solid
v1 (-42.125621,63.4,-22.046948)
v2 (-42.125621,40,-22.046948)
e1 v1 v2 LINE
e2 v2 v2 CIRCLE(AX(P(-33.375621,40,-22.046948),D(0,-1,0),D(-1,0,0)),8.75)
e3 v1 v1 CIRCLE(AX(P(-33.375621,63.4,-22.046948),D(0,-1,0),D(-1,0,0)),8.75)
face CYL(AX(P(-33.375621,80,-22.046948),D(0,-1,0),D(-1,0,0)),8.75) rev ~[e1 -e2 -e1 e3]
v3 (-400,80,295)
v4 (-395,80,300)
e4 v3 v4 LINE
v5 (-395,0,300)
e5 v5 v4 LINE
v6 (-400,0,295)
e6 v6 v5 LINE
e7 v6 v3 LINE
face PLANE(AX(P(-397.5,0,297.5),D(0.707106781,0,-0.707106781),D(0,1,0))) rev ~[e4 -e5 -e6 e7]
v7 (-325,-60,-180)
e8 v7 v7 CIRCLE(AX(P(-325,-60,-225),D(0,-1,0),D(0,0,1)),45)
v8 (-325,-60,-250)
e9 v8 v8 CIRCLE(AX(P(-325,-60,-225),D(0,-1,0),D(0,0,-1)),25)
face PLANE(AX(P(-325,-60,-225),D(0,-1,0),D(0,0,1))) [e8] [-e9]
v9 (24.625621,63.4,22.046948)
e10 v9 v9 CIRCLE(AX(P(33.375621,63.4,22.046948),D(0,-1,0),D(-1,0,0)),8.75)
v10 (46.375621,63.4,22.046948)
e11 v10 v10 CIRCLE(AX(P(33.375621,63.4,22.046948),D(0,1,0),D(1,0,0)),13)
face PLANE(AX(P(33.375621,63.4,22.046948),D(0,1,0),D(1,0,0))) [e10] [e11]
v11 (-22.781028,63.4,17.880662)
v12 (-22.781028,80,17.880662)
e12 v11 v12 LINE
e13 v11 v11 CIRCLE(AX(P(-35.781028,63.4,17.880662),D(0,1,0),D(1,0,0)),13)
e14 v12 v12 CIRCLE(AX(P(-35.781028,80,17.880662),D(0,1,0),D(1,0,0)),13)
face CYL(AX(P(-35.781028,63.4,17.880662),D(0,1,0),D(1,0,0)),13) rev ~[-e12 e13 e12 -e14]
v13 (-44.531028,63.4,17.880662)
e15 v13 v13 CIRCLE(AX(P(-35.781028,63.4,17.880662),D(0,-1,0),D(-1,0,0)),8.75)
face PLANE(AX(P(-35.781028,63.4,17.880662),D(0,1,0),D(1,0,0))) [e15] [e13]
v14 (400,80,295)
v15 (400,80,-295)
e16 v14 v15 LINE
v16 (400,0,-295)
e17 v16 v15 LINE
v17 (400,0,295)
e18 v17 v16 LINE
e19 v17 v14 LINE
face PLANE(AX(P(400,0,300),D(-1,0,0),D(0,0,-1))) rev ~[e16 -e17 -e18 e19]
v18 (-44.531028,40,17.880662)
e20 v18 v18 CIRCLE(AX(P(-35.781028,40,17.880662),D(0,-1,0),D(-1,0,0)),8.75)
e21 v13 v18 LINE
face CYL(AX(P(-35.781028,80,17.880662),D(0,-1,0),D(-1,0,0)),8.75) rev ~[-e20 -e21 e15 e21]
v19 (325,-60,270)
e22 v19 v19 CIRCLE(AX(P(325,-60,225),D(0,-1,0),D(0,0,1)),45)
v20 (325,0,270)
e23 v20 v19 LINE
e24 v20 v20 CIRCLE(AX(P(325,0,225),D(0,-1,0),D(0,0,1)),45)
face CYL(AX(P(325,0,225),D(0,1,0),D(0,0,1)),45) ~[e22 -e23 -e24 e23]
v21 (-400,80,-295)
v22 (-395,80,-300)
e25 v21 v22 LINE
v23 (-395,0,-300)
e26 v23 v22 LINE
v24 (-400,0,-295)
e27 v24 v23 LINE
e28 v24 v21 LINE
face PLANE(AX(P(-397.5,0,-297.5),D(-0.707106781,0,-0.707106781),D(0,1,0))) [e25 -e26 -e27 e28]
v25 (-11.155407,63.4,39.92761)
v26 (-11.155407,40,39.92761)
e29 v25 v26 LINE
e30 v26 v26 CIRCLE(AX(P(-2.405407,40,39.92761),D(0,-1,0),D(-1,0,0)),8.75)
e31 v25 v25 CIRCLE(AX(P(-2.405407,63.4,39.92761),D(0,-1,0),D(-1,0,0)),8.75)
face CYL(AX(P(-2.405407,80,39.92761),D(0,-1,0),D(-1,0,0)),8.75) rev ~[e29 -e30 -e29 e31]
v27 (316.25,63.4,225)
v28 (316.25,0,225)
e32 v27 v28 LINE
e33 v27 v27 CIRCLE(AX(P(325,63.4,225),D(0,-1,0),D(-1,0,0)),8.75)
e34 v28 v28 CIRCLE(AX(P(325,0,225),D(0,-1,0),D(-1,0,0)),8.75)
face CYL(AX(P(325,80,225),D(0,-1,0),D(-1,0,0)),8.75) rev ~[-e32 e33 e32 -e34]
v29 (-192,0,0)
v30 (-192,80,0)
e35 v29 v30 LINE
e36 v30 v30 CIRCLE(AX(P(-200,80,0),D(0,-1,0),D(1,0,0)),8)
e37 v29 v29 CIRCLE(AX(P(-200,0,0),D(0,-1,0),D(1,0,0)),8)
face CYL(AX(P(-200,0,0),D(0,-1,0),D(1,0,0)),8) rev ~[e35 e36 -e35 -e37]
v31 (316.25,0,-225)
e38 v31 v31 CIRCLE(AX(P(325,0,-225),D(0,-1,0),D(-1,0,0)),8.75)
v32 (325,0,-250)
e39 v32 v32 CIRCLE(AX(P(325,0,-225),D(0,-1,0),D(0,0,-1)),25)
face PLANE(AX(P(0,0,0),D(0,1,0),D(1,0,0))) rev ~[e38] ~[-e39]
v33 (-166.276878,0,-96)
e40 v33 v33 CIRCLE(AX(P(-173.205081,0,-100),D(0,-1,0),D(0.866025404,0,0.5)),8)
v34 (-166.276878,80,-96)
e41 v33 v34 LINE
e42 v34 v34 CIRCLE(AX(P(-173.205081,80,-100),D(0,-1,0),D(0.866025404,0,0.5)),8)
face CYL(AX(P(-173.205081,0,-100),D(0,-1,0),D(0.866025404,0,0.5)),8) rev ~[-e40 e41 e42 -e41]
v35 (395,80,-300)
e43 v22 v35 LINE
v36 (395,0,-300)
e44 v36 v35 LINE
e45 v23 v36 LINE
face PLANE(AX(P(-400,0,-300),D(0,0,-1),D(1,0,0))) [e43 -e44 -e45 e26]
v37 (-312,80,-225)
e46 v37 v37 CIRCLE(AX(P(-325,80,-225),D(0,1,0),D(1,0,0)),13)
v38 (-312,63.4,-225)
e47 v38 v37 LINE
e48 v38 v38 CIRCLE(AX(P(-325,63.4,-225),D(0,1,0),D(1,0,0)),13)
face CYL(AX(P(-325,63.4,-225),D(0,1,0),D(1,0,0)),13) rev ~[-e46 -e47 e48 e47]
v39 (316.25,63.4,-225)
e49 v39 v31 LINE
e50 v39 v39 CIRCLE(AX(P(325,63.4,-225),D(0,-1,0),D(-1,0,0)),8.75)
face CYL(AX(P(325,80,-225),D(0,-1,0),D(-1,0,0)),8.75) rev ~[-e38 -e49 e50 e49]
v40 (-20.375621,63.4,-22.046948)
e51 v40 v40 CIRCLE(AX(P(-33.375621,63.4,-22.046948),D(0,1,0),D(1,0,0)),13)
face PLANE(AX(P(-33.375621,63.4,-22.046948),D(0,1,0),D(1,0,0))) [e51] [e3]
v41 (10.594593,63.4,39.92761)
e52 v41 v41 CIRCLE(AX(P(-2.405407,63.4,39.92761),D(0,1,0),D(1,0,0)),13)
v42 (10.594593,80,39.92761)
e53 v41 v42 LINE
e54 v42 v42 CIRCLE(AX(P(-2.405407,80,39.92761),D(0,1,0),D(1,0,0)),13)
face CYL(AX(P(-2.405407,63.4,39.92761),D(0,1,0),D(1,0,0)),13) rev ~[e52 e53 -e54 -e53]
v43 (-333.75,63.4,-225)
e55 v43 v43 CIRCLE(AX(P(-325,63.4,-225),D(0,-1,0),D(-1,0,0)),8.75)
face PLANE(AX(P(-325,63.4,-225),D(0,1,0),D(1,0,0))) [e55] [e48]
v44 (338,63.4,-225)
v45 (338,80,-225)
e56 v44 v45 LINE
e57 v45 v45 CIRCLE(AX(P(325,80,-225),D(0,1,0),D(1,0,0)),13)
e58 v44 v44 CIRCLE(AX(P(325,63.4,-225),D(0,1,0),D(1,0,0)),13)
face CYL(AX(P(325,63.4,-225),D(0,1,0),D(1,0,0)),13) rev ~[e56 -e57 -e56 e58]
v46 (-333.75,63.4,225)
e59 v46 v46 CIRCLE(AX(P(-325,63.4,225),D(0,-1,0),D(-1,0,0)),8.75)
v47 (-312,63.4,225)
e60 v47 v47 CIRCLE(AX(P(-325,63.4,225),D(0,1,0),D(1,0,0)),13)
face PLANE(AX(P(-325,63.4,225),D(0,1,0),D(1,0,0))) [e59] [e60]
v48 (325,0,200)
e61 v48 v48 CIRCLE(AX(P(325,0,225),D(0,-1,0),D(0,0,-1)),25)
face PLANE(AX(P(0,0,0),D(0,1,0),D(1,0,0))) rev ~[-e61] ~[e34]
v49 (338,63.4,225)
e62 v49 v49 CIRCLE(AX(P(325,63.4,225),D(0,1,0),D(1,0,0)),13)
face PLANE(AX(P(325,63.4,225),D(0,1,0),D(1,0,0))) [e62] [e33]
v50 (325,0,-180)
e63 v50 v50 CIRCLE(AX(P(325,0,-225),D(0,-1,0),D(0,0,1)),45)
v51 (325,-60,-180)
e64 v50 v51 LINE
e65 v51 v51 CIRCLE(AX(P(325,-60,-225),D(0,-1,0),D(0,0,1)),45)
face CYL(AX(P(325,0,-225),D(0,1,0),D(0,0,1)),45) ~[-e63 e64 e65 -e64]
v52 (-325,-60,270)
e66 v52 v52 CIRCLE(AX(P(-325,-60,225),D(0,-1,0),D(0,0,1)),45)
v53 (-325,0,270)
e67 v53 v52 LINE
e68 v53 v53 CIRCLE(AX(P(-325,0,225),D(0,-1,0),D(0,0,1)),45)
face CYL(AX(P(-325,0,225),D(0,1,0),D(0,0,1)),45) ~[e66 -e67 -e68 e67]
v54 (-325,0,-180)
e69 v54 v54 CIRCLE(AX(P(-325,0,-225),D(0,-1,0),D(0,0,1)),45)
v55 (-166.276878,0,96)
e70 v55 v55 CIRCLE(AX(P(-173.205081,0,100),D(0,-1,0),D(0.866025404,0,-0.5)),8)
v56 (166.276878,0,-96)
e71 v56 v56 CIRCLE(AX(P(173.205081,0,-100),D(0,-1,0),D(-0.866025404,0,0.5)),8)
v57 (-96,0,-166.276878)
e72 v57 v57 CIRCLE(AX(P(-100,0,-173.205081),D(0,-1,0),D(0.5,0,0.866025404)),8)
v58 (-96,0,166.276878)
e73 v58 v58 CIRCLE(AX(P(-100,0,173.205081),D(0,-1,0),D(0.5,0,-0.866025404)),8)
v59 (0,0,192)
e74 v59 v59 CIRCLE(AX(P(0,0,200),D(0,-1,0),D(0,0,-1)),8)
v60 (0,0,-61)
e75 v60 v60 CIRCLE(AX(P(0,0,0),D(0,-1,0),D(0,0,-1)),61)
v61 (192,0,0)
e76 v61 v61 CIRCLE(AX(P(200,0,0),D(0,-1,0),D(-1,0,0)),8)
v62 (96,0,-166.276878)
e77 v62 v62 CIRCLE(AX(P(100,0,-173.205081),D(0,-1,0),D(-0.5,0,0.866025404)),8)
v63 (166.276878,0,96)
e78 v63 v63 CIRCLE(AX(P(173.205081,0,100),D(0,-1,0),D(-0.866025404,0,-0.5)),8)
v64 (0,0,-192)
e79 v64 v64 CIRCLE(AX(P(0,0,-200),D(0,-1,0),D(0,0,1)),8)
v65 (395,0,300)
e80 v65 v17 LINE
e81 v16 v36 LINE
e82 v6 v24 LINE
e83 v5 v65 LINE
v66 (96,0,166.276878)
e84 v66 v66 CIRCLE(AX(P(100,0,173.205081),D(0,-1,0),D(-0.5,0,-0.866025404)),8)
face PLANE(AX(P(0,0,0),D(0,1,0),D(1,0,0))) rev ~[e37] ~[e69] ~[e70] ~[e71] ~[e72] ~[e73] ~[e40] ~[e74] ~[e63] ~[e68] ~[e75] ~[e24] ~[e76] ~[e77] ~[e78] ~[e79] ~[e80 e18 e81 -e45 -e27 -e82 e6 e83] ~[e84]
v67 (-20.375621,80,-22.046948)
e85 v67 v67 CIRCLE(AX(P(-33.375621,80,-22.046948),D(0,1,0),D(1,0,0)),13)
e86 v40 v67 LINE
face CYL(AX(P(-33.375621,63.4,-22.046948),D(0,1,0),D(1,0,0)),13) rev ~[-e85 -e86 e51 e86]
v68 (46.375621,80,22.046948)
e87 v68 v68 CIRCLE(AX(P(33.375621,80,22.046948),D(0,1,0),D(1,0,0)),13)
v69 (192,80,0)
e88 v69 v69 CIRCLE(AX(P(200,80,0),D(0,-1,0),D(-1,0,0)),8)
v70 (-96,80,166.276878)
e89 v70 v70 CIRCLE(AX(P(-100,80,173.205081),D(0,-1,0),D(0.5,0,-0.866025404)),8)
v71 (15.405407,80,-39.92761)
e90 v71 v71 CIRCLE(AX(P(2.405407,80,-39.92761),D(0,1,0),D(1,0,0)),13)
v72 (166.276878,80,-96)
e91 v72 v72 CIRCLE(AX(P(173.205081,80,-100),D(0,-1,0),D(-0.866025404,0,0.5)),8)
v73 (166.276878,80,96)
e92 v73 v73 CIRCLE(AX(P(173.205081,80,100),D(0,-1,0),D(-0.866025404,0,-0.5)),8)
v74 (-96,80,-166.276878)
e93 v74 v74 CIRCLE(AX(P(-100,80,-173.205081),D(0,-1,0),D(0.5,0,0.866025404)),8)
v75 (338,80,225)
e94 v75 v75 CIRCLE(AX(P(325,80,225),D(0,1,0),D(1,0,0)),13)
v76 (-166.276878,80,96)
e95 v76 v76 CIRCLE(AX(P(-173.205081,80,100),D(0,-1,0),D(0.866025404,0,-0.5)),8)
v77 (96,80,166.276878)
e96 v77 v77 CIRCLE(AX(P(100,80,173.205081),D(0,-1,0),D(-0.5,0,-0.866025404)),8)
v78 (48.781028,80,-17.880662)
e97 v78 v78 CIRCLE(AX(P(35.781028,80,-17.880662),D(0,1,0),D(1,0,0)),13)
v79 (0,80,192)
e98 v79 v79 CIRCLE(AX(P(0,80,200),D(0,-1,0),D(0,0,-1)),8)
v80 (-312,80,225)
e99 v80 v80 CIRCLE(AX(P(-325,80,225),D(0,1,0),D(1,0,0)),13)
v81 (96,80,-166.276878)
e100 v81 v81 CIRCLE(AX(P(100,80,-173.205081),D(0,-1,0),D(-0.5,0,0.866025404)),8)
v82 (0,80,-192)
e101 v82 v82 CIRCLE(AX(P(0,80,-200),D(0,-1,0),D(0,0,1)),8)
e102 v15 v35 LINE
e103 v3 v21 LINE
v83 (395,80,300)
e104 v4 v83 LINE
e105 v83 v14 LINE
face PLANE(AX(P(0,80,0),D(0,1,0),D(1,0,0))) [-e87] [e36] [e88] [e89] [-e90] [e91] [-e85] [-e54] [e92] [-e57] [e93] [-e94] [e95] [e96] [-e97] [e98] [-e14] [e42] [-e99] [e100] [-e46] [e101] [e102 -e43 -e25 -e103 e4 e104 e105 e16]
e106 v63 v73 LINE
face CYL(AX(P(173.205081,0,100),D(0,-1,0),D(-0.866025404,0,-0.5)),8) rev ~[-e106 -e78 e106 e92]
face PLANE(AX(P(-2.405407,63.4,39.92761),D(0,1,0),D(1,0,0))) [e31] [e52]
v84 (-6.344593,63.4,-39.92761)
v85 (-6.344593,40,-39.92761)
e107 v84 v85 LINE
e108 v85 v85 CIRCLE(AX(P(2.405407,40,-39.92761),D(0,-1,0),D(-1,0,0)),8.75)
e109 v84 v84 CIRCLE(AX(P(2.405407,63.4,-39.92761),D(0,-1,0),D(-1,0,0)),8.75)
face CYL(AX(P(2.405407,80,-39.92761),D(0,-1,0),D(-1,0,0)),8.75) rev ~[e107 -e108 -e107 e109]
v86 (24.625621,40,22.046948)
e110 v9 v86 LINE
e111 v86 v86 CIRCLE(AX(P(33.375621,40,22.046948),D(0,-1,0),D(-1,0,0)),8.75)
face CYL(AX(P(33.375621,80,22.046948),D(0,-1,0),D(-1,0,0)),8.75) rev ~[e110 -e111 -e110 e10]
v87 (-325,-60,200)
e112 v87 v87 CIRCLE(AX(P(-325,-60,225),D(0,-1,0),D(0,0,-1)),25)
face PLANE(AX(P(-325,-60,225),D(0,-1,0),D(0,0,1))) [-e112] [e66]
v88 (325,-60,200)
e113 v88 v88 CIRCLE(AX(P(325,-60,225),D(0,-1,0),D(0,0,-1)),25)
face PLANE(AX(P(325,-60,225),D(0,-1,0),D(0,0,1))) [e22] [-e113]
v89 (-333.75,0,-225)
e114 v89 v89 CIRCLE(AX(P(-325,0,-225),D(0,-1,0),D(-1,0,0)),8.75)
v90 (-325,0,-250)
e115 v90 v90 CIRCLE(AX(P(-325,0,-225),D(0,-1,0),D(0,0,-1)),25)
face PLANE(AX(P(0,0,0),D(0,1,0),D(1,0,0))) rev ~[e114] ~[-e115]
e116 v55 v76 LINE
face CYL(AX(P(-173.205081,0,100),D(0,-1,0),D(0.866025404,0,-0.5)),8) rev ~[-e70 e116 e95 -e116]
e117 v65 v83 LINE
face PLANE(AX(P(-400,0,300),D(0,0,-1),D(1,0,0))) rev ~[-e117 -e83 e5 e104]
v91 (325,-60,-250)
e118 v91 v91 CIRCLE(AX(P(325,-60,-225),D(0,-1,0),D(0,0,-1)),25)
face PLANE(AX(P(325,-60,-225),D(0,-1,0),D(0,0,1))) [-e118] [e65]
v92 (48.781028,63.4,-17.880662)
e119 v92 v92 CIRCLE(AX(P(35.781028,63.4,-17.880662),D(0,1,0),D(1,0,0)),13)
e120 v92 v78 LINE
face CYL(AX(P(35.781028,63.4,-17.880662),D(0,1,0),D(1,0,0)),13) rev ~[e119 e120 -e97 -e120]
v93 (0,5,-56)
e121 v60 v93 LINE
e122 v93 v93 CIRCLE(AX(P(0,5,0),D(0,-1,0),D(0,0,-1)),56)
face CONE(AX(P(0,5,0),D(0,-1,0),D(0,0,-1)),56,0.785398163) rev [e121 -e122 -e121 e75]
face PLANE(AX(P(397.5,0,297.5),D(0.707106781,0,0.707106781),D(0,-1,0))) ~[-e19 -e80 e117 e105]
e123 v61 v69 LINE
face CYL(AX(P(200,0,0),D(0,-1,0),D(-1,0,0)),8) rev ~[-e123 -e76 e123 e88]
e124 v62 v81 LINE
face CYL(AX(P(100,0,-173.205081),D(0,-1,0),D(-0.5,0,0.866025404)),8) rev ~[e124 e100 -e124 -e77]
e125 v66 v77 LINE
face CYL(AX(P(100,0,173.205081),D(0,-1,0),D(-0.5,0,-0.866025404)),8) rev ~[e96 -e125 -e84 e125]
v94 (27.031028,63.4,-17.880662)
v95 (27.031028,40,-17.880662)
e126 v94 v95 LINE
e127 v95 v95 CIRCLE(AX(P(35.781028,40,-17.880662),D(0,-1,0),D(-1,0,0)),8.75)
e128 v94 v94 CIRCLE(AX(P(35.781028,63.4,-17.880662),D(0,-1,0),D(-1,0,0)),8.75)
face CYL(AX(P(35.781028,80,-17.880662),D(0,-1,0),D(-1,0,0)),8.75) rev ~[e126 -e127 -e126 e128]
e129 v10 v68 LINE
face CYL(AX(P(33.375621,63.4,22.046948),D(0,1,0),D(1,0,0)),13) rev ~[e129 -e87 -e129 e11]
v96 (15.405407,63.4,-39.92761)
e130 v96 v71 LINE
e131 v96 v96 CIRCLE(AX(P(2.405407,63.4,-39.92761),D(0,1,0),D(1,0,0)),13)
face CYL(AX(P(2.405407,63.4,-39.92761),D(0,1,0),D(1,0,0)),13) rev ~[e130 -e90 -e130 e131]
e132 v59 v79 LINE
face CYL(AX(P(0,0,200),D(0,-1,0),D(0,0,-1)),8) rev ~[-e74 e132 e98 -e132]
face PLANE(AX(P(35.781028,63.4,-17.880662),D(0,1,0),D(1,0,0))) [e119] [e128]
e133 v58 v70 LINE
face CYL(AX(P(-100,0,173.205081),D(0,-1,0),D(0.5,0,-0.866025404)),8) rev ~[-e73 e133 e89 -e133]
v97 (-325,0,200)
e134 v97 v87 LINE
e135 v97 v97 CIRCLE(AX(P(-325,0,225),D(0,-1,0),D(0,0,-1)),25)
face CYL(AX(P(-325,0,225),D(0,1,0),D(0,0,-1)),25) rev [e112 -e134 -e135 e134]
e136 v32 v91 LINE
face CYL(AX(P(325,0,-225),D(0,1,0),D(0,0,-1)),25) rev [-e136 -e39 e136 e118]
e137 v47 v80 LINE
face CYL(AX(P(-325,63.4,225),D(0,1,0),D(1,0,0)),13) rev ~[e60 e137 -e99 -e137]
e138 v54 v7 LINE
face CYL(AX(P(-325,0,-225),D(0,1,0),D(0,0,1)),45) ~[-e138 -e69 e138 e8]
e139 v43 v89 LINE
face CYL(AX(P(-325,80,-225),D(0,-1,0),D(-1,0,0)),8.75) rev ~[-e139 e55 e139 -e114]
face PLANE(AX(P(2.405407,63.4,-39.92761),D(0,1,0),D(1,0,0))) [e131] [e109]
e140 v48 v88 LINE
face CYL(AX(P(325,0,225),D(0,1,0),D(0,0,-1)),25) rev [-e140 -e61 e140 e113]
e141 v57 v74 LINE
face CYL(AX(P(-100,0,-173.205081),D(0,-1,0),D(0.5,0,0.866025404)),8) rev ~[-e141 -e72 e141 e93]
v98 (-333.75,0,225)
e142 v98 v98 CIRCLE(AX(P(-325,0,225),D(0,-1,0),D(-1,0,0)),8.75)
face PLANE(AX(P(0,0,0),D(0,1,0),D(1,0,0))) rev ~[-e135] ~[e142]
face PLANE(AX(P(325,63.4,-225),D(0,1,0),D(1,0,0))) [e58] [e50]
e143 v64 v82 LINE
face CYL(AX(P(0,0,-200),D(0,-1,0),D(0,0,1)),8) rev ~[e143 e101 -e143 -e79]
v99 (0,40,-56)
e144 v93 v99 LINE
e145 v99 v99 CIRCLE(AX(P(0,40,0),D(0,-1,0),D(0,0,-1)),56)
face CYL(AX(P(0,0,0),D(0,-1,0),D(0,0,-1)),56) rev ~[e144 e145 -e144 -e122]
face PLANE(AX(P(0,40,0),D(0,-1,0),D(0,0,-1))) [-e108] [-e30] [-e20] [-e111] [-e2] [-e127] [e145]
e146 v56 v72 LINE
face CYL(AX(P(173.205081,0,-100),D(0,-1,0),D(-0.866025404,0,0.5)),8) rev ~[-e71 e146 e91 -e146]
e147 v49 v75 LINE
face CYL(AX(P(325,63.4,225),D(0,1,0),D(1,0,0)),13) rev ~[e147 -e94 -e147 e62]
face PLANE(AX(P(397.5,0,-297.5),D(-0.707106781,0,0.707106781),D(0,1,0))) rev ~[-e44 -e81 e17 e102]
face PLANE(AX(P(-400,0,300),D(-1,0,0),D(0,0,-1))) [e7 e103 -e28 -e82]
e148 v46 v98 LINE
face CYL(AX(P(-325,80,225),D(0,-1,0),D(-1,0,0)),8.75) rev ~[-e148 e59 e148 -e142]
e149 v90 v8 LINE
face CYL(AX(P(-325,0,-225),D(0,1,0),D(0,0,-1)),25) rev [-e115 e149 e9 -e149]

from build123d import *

# Parameters (mm, degrees)
SKETCH1_W                                            = 800
SKETCH1_H                                            = 600
BOSS_EXTRUDE1_DEPTH                                  = 80
CHAMFER1_SIZE                                        = 5
CBORE_FOR_M16_HEX_SOCKET_HEAD_CAP_SCREW1_D           = 17.5
CBORE_FOR_M16_HEX_SOCKET_HEAD_CAP_SCREW1_CBORE_D     = 26
CBORE_FOR_M16_HEX_SOCKET_HEAD_CAP_SCREW1_CBORE_DEPTH = 16.6
SKETCH4_R                                            = 56
CUT_EXTRUDE1_DEPTH                                   = 40
CHAMFER2_SIZE                                        = 5
SKETCH6_R                                            = 45
SKETCH6_R_2                                          = 25
BOSS_EXTRUDE2_DEPTH                                  = 60
CBORE_FOR_M16_HEX_SOCKET_HEAD_CAP_SCREW2_D           = 17.5
CBORE_FOR_M16_HEX_SOCKET_HEAD_CAP_SCREW2_CBORE_D     = 26
CBORE_FOR_M16_HEX_SOCKET_HEAD_CAP_SCREW2_CBORE_DEPTH = 16.6
SKETCH10_R                                           = 8
CUT_EXTRUDE2_DEPTH                                   = 507.359556047
CIRPATTERN1_COUNT                                    = 12


with BuildPart() as part:
    # Sketch1 → Boss-Extrude1 (new body)
    with BuildSketch(Plane(origin=(0, 0, 0), x_dir=(1, 0, 0), z_dir=(0, 1, 0))):
        Rectangle(SKETCH1_W, SKETCH1_H)
    extrude(amount=BOSS_EXTRUDE1_DEPTH)

    # Chamfer1
    chamfer1_edges = [part.edges().sort_by_distance(p)[0] for p in [
        (400, 40, 300),
        (-400, 40, 300),
        (-400, 40, -300),
        (400, 40, -300),
    ]]
    chamfer(chamfer1_edges, length=CHAMFER1_SIZE)

    # CBORE for M16 Hex Socket Head Cap Screw1 (through all)
    with Locations(Plane(origin=(0, 80, 0), x_dir=(1, 0, 0), z_dir=(0, 1, 0))):
        with Locations((2.405406629, 39.927609732), (35.781027655, 17.880661619), (33.375621026, -22.046948113), (-2.405406629, -39.927609732), (-35.781027655, -17.880661619), (-33.375621026, 22.046948113)):
            CounterBoreHole(CBORE_FOR_M16_HEX_SOCKET_HEAD_CAP_SCREW1_D / 2, CBORE_FOR_M16_HEX_SOCKET_HEAD_CAP_SCREW1_CBORE_D / 2, CBORE_FOR_M16_HEX_SOCKET_HEAD_CAP_SCREW1_CBORE_DEPTH)

    # Sketch4 → Cut-Extrude1 (cut)
    with BuildSketch(Plane.XZ):
        with Locations(Location((0, 0, 0), (0, 0, 270))):
            Circle(SKETCH4_R)
    extrude(amount=-CUT_EXTRUDE1_DEPTH, mode=Mode.SUBTRACT)

    # Chamfer2
    chamfer2_edges = [part.edges().sort_by_distance(p)[0] for p in [
        (0, 0, 56),
    ]]
    chamfer(chamfer2_edges, length=CHAMFER2_SIZE)

    # Sketch6 → Boss-Extrude2 (add)
    # profile 1 of 4: a face of its own
    with BuildSketch(Plane.XZ):
        with Locations(Location((-325, 225, 0), (0, 0, 90))):
            Circle(SKETCH6_R)
        with Locations(Location((-325, 225, 0), (0, 0, 270))):
            Circle(SKETCH6_R_2, mode=Mode.SUBTRACT)
    # profile 2 of 4: a face of its own
    with BuildSketch(Plane.XZ):
        with Locations(Location((325, 225, 0), (0, 0, 90))):
            Circle(SKETCH6_R)
        with Locations(Location((325, 225, 0), (0, 0, 270))):
            Circle(SKETCH6_R_2, mode=Mode.SUBTRACT)
    # profile 3 of 4: a face of its own
    with BuildSketch(Plane.XZ):
        with Locations(Location((-325, -225, 0), (0, 0, 90))):
            Circle(SKETCH6_R)
        with Locations(Location((-325, -225, 0), (0, 0, 270))):
            Circle(SKETCH6_R_2, mode=Mode.SUBTRACT)
    # profile 4 of 4: a face of its own
    with BuildSketch(Plane.XZ):
        with Locations(Location((325, -225, 0), (0, 0, 90))):
            Circle(SKETCH6_R)
        with Locations(Location((325, -225, 0), (0, 0, 270))):
            Circle(SKETCH6_R_2, mode=Mode.SUBTRACT)
    extrude(amount=BOSS_EXTRUDE2_DEPTH)

    # CBORE for M16 Hex Socket Head Cap Screw2 (through all)
    with Locations(Plane(origin=(0, 80, 0), x_dir=(1, 0, 0), z_dir=(0, 1, 0))):
        with Locations((-325, -225), (-325, 225), (325, 225), (325, -225)):
            CounterBoreHole(CBORE_FOR_M16_HEX_SOCKET_HEAD_CAP_SCREW2_D / 2, CBORE_FOR_M16_HEX_SOCKET_HEAD_CAP_SCREW2_CBORE_D / 2, CBORE_FOR_M16_HEX_SOCKET_HEAD_CAP_SCREW2_CBORE_DEPTH)

    # Sketch10 → Cut-Extrude2 (cut, through all)
    with BuildSketch(Plane.XZ):
        with Locations(Location((0, 200, 0), (0, 0, 270))):
            Circle(SKETCH10_R)
    cut_extrude2 = extrude(amount=-CUT_EXTRUDE2_DEPTH, mode=Mode.SUBTRACT)

    # CirPattern1: Cut-Extrude2 ×12 about axis
    cirpattern1_axis = Axis((0, 0, 0), (0, 1, 0))
    for i in range(1, CIRPATTERN1_COUNT):
        add(cut_extrude2.rotate(cirpattern1_axis, i * 360 / CIRPATTERN1_COUNT), mode=Mode.SUBTRACT)


solid = part.part
